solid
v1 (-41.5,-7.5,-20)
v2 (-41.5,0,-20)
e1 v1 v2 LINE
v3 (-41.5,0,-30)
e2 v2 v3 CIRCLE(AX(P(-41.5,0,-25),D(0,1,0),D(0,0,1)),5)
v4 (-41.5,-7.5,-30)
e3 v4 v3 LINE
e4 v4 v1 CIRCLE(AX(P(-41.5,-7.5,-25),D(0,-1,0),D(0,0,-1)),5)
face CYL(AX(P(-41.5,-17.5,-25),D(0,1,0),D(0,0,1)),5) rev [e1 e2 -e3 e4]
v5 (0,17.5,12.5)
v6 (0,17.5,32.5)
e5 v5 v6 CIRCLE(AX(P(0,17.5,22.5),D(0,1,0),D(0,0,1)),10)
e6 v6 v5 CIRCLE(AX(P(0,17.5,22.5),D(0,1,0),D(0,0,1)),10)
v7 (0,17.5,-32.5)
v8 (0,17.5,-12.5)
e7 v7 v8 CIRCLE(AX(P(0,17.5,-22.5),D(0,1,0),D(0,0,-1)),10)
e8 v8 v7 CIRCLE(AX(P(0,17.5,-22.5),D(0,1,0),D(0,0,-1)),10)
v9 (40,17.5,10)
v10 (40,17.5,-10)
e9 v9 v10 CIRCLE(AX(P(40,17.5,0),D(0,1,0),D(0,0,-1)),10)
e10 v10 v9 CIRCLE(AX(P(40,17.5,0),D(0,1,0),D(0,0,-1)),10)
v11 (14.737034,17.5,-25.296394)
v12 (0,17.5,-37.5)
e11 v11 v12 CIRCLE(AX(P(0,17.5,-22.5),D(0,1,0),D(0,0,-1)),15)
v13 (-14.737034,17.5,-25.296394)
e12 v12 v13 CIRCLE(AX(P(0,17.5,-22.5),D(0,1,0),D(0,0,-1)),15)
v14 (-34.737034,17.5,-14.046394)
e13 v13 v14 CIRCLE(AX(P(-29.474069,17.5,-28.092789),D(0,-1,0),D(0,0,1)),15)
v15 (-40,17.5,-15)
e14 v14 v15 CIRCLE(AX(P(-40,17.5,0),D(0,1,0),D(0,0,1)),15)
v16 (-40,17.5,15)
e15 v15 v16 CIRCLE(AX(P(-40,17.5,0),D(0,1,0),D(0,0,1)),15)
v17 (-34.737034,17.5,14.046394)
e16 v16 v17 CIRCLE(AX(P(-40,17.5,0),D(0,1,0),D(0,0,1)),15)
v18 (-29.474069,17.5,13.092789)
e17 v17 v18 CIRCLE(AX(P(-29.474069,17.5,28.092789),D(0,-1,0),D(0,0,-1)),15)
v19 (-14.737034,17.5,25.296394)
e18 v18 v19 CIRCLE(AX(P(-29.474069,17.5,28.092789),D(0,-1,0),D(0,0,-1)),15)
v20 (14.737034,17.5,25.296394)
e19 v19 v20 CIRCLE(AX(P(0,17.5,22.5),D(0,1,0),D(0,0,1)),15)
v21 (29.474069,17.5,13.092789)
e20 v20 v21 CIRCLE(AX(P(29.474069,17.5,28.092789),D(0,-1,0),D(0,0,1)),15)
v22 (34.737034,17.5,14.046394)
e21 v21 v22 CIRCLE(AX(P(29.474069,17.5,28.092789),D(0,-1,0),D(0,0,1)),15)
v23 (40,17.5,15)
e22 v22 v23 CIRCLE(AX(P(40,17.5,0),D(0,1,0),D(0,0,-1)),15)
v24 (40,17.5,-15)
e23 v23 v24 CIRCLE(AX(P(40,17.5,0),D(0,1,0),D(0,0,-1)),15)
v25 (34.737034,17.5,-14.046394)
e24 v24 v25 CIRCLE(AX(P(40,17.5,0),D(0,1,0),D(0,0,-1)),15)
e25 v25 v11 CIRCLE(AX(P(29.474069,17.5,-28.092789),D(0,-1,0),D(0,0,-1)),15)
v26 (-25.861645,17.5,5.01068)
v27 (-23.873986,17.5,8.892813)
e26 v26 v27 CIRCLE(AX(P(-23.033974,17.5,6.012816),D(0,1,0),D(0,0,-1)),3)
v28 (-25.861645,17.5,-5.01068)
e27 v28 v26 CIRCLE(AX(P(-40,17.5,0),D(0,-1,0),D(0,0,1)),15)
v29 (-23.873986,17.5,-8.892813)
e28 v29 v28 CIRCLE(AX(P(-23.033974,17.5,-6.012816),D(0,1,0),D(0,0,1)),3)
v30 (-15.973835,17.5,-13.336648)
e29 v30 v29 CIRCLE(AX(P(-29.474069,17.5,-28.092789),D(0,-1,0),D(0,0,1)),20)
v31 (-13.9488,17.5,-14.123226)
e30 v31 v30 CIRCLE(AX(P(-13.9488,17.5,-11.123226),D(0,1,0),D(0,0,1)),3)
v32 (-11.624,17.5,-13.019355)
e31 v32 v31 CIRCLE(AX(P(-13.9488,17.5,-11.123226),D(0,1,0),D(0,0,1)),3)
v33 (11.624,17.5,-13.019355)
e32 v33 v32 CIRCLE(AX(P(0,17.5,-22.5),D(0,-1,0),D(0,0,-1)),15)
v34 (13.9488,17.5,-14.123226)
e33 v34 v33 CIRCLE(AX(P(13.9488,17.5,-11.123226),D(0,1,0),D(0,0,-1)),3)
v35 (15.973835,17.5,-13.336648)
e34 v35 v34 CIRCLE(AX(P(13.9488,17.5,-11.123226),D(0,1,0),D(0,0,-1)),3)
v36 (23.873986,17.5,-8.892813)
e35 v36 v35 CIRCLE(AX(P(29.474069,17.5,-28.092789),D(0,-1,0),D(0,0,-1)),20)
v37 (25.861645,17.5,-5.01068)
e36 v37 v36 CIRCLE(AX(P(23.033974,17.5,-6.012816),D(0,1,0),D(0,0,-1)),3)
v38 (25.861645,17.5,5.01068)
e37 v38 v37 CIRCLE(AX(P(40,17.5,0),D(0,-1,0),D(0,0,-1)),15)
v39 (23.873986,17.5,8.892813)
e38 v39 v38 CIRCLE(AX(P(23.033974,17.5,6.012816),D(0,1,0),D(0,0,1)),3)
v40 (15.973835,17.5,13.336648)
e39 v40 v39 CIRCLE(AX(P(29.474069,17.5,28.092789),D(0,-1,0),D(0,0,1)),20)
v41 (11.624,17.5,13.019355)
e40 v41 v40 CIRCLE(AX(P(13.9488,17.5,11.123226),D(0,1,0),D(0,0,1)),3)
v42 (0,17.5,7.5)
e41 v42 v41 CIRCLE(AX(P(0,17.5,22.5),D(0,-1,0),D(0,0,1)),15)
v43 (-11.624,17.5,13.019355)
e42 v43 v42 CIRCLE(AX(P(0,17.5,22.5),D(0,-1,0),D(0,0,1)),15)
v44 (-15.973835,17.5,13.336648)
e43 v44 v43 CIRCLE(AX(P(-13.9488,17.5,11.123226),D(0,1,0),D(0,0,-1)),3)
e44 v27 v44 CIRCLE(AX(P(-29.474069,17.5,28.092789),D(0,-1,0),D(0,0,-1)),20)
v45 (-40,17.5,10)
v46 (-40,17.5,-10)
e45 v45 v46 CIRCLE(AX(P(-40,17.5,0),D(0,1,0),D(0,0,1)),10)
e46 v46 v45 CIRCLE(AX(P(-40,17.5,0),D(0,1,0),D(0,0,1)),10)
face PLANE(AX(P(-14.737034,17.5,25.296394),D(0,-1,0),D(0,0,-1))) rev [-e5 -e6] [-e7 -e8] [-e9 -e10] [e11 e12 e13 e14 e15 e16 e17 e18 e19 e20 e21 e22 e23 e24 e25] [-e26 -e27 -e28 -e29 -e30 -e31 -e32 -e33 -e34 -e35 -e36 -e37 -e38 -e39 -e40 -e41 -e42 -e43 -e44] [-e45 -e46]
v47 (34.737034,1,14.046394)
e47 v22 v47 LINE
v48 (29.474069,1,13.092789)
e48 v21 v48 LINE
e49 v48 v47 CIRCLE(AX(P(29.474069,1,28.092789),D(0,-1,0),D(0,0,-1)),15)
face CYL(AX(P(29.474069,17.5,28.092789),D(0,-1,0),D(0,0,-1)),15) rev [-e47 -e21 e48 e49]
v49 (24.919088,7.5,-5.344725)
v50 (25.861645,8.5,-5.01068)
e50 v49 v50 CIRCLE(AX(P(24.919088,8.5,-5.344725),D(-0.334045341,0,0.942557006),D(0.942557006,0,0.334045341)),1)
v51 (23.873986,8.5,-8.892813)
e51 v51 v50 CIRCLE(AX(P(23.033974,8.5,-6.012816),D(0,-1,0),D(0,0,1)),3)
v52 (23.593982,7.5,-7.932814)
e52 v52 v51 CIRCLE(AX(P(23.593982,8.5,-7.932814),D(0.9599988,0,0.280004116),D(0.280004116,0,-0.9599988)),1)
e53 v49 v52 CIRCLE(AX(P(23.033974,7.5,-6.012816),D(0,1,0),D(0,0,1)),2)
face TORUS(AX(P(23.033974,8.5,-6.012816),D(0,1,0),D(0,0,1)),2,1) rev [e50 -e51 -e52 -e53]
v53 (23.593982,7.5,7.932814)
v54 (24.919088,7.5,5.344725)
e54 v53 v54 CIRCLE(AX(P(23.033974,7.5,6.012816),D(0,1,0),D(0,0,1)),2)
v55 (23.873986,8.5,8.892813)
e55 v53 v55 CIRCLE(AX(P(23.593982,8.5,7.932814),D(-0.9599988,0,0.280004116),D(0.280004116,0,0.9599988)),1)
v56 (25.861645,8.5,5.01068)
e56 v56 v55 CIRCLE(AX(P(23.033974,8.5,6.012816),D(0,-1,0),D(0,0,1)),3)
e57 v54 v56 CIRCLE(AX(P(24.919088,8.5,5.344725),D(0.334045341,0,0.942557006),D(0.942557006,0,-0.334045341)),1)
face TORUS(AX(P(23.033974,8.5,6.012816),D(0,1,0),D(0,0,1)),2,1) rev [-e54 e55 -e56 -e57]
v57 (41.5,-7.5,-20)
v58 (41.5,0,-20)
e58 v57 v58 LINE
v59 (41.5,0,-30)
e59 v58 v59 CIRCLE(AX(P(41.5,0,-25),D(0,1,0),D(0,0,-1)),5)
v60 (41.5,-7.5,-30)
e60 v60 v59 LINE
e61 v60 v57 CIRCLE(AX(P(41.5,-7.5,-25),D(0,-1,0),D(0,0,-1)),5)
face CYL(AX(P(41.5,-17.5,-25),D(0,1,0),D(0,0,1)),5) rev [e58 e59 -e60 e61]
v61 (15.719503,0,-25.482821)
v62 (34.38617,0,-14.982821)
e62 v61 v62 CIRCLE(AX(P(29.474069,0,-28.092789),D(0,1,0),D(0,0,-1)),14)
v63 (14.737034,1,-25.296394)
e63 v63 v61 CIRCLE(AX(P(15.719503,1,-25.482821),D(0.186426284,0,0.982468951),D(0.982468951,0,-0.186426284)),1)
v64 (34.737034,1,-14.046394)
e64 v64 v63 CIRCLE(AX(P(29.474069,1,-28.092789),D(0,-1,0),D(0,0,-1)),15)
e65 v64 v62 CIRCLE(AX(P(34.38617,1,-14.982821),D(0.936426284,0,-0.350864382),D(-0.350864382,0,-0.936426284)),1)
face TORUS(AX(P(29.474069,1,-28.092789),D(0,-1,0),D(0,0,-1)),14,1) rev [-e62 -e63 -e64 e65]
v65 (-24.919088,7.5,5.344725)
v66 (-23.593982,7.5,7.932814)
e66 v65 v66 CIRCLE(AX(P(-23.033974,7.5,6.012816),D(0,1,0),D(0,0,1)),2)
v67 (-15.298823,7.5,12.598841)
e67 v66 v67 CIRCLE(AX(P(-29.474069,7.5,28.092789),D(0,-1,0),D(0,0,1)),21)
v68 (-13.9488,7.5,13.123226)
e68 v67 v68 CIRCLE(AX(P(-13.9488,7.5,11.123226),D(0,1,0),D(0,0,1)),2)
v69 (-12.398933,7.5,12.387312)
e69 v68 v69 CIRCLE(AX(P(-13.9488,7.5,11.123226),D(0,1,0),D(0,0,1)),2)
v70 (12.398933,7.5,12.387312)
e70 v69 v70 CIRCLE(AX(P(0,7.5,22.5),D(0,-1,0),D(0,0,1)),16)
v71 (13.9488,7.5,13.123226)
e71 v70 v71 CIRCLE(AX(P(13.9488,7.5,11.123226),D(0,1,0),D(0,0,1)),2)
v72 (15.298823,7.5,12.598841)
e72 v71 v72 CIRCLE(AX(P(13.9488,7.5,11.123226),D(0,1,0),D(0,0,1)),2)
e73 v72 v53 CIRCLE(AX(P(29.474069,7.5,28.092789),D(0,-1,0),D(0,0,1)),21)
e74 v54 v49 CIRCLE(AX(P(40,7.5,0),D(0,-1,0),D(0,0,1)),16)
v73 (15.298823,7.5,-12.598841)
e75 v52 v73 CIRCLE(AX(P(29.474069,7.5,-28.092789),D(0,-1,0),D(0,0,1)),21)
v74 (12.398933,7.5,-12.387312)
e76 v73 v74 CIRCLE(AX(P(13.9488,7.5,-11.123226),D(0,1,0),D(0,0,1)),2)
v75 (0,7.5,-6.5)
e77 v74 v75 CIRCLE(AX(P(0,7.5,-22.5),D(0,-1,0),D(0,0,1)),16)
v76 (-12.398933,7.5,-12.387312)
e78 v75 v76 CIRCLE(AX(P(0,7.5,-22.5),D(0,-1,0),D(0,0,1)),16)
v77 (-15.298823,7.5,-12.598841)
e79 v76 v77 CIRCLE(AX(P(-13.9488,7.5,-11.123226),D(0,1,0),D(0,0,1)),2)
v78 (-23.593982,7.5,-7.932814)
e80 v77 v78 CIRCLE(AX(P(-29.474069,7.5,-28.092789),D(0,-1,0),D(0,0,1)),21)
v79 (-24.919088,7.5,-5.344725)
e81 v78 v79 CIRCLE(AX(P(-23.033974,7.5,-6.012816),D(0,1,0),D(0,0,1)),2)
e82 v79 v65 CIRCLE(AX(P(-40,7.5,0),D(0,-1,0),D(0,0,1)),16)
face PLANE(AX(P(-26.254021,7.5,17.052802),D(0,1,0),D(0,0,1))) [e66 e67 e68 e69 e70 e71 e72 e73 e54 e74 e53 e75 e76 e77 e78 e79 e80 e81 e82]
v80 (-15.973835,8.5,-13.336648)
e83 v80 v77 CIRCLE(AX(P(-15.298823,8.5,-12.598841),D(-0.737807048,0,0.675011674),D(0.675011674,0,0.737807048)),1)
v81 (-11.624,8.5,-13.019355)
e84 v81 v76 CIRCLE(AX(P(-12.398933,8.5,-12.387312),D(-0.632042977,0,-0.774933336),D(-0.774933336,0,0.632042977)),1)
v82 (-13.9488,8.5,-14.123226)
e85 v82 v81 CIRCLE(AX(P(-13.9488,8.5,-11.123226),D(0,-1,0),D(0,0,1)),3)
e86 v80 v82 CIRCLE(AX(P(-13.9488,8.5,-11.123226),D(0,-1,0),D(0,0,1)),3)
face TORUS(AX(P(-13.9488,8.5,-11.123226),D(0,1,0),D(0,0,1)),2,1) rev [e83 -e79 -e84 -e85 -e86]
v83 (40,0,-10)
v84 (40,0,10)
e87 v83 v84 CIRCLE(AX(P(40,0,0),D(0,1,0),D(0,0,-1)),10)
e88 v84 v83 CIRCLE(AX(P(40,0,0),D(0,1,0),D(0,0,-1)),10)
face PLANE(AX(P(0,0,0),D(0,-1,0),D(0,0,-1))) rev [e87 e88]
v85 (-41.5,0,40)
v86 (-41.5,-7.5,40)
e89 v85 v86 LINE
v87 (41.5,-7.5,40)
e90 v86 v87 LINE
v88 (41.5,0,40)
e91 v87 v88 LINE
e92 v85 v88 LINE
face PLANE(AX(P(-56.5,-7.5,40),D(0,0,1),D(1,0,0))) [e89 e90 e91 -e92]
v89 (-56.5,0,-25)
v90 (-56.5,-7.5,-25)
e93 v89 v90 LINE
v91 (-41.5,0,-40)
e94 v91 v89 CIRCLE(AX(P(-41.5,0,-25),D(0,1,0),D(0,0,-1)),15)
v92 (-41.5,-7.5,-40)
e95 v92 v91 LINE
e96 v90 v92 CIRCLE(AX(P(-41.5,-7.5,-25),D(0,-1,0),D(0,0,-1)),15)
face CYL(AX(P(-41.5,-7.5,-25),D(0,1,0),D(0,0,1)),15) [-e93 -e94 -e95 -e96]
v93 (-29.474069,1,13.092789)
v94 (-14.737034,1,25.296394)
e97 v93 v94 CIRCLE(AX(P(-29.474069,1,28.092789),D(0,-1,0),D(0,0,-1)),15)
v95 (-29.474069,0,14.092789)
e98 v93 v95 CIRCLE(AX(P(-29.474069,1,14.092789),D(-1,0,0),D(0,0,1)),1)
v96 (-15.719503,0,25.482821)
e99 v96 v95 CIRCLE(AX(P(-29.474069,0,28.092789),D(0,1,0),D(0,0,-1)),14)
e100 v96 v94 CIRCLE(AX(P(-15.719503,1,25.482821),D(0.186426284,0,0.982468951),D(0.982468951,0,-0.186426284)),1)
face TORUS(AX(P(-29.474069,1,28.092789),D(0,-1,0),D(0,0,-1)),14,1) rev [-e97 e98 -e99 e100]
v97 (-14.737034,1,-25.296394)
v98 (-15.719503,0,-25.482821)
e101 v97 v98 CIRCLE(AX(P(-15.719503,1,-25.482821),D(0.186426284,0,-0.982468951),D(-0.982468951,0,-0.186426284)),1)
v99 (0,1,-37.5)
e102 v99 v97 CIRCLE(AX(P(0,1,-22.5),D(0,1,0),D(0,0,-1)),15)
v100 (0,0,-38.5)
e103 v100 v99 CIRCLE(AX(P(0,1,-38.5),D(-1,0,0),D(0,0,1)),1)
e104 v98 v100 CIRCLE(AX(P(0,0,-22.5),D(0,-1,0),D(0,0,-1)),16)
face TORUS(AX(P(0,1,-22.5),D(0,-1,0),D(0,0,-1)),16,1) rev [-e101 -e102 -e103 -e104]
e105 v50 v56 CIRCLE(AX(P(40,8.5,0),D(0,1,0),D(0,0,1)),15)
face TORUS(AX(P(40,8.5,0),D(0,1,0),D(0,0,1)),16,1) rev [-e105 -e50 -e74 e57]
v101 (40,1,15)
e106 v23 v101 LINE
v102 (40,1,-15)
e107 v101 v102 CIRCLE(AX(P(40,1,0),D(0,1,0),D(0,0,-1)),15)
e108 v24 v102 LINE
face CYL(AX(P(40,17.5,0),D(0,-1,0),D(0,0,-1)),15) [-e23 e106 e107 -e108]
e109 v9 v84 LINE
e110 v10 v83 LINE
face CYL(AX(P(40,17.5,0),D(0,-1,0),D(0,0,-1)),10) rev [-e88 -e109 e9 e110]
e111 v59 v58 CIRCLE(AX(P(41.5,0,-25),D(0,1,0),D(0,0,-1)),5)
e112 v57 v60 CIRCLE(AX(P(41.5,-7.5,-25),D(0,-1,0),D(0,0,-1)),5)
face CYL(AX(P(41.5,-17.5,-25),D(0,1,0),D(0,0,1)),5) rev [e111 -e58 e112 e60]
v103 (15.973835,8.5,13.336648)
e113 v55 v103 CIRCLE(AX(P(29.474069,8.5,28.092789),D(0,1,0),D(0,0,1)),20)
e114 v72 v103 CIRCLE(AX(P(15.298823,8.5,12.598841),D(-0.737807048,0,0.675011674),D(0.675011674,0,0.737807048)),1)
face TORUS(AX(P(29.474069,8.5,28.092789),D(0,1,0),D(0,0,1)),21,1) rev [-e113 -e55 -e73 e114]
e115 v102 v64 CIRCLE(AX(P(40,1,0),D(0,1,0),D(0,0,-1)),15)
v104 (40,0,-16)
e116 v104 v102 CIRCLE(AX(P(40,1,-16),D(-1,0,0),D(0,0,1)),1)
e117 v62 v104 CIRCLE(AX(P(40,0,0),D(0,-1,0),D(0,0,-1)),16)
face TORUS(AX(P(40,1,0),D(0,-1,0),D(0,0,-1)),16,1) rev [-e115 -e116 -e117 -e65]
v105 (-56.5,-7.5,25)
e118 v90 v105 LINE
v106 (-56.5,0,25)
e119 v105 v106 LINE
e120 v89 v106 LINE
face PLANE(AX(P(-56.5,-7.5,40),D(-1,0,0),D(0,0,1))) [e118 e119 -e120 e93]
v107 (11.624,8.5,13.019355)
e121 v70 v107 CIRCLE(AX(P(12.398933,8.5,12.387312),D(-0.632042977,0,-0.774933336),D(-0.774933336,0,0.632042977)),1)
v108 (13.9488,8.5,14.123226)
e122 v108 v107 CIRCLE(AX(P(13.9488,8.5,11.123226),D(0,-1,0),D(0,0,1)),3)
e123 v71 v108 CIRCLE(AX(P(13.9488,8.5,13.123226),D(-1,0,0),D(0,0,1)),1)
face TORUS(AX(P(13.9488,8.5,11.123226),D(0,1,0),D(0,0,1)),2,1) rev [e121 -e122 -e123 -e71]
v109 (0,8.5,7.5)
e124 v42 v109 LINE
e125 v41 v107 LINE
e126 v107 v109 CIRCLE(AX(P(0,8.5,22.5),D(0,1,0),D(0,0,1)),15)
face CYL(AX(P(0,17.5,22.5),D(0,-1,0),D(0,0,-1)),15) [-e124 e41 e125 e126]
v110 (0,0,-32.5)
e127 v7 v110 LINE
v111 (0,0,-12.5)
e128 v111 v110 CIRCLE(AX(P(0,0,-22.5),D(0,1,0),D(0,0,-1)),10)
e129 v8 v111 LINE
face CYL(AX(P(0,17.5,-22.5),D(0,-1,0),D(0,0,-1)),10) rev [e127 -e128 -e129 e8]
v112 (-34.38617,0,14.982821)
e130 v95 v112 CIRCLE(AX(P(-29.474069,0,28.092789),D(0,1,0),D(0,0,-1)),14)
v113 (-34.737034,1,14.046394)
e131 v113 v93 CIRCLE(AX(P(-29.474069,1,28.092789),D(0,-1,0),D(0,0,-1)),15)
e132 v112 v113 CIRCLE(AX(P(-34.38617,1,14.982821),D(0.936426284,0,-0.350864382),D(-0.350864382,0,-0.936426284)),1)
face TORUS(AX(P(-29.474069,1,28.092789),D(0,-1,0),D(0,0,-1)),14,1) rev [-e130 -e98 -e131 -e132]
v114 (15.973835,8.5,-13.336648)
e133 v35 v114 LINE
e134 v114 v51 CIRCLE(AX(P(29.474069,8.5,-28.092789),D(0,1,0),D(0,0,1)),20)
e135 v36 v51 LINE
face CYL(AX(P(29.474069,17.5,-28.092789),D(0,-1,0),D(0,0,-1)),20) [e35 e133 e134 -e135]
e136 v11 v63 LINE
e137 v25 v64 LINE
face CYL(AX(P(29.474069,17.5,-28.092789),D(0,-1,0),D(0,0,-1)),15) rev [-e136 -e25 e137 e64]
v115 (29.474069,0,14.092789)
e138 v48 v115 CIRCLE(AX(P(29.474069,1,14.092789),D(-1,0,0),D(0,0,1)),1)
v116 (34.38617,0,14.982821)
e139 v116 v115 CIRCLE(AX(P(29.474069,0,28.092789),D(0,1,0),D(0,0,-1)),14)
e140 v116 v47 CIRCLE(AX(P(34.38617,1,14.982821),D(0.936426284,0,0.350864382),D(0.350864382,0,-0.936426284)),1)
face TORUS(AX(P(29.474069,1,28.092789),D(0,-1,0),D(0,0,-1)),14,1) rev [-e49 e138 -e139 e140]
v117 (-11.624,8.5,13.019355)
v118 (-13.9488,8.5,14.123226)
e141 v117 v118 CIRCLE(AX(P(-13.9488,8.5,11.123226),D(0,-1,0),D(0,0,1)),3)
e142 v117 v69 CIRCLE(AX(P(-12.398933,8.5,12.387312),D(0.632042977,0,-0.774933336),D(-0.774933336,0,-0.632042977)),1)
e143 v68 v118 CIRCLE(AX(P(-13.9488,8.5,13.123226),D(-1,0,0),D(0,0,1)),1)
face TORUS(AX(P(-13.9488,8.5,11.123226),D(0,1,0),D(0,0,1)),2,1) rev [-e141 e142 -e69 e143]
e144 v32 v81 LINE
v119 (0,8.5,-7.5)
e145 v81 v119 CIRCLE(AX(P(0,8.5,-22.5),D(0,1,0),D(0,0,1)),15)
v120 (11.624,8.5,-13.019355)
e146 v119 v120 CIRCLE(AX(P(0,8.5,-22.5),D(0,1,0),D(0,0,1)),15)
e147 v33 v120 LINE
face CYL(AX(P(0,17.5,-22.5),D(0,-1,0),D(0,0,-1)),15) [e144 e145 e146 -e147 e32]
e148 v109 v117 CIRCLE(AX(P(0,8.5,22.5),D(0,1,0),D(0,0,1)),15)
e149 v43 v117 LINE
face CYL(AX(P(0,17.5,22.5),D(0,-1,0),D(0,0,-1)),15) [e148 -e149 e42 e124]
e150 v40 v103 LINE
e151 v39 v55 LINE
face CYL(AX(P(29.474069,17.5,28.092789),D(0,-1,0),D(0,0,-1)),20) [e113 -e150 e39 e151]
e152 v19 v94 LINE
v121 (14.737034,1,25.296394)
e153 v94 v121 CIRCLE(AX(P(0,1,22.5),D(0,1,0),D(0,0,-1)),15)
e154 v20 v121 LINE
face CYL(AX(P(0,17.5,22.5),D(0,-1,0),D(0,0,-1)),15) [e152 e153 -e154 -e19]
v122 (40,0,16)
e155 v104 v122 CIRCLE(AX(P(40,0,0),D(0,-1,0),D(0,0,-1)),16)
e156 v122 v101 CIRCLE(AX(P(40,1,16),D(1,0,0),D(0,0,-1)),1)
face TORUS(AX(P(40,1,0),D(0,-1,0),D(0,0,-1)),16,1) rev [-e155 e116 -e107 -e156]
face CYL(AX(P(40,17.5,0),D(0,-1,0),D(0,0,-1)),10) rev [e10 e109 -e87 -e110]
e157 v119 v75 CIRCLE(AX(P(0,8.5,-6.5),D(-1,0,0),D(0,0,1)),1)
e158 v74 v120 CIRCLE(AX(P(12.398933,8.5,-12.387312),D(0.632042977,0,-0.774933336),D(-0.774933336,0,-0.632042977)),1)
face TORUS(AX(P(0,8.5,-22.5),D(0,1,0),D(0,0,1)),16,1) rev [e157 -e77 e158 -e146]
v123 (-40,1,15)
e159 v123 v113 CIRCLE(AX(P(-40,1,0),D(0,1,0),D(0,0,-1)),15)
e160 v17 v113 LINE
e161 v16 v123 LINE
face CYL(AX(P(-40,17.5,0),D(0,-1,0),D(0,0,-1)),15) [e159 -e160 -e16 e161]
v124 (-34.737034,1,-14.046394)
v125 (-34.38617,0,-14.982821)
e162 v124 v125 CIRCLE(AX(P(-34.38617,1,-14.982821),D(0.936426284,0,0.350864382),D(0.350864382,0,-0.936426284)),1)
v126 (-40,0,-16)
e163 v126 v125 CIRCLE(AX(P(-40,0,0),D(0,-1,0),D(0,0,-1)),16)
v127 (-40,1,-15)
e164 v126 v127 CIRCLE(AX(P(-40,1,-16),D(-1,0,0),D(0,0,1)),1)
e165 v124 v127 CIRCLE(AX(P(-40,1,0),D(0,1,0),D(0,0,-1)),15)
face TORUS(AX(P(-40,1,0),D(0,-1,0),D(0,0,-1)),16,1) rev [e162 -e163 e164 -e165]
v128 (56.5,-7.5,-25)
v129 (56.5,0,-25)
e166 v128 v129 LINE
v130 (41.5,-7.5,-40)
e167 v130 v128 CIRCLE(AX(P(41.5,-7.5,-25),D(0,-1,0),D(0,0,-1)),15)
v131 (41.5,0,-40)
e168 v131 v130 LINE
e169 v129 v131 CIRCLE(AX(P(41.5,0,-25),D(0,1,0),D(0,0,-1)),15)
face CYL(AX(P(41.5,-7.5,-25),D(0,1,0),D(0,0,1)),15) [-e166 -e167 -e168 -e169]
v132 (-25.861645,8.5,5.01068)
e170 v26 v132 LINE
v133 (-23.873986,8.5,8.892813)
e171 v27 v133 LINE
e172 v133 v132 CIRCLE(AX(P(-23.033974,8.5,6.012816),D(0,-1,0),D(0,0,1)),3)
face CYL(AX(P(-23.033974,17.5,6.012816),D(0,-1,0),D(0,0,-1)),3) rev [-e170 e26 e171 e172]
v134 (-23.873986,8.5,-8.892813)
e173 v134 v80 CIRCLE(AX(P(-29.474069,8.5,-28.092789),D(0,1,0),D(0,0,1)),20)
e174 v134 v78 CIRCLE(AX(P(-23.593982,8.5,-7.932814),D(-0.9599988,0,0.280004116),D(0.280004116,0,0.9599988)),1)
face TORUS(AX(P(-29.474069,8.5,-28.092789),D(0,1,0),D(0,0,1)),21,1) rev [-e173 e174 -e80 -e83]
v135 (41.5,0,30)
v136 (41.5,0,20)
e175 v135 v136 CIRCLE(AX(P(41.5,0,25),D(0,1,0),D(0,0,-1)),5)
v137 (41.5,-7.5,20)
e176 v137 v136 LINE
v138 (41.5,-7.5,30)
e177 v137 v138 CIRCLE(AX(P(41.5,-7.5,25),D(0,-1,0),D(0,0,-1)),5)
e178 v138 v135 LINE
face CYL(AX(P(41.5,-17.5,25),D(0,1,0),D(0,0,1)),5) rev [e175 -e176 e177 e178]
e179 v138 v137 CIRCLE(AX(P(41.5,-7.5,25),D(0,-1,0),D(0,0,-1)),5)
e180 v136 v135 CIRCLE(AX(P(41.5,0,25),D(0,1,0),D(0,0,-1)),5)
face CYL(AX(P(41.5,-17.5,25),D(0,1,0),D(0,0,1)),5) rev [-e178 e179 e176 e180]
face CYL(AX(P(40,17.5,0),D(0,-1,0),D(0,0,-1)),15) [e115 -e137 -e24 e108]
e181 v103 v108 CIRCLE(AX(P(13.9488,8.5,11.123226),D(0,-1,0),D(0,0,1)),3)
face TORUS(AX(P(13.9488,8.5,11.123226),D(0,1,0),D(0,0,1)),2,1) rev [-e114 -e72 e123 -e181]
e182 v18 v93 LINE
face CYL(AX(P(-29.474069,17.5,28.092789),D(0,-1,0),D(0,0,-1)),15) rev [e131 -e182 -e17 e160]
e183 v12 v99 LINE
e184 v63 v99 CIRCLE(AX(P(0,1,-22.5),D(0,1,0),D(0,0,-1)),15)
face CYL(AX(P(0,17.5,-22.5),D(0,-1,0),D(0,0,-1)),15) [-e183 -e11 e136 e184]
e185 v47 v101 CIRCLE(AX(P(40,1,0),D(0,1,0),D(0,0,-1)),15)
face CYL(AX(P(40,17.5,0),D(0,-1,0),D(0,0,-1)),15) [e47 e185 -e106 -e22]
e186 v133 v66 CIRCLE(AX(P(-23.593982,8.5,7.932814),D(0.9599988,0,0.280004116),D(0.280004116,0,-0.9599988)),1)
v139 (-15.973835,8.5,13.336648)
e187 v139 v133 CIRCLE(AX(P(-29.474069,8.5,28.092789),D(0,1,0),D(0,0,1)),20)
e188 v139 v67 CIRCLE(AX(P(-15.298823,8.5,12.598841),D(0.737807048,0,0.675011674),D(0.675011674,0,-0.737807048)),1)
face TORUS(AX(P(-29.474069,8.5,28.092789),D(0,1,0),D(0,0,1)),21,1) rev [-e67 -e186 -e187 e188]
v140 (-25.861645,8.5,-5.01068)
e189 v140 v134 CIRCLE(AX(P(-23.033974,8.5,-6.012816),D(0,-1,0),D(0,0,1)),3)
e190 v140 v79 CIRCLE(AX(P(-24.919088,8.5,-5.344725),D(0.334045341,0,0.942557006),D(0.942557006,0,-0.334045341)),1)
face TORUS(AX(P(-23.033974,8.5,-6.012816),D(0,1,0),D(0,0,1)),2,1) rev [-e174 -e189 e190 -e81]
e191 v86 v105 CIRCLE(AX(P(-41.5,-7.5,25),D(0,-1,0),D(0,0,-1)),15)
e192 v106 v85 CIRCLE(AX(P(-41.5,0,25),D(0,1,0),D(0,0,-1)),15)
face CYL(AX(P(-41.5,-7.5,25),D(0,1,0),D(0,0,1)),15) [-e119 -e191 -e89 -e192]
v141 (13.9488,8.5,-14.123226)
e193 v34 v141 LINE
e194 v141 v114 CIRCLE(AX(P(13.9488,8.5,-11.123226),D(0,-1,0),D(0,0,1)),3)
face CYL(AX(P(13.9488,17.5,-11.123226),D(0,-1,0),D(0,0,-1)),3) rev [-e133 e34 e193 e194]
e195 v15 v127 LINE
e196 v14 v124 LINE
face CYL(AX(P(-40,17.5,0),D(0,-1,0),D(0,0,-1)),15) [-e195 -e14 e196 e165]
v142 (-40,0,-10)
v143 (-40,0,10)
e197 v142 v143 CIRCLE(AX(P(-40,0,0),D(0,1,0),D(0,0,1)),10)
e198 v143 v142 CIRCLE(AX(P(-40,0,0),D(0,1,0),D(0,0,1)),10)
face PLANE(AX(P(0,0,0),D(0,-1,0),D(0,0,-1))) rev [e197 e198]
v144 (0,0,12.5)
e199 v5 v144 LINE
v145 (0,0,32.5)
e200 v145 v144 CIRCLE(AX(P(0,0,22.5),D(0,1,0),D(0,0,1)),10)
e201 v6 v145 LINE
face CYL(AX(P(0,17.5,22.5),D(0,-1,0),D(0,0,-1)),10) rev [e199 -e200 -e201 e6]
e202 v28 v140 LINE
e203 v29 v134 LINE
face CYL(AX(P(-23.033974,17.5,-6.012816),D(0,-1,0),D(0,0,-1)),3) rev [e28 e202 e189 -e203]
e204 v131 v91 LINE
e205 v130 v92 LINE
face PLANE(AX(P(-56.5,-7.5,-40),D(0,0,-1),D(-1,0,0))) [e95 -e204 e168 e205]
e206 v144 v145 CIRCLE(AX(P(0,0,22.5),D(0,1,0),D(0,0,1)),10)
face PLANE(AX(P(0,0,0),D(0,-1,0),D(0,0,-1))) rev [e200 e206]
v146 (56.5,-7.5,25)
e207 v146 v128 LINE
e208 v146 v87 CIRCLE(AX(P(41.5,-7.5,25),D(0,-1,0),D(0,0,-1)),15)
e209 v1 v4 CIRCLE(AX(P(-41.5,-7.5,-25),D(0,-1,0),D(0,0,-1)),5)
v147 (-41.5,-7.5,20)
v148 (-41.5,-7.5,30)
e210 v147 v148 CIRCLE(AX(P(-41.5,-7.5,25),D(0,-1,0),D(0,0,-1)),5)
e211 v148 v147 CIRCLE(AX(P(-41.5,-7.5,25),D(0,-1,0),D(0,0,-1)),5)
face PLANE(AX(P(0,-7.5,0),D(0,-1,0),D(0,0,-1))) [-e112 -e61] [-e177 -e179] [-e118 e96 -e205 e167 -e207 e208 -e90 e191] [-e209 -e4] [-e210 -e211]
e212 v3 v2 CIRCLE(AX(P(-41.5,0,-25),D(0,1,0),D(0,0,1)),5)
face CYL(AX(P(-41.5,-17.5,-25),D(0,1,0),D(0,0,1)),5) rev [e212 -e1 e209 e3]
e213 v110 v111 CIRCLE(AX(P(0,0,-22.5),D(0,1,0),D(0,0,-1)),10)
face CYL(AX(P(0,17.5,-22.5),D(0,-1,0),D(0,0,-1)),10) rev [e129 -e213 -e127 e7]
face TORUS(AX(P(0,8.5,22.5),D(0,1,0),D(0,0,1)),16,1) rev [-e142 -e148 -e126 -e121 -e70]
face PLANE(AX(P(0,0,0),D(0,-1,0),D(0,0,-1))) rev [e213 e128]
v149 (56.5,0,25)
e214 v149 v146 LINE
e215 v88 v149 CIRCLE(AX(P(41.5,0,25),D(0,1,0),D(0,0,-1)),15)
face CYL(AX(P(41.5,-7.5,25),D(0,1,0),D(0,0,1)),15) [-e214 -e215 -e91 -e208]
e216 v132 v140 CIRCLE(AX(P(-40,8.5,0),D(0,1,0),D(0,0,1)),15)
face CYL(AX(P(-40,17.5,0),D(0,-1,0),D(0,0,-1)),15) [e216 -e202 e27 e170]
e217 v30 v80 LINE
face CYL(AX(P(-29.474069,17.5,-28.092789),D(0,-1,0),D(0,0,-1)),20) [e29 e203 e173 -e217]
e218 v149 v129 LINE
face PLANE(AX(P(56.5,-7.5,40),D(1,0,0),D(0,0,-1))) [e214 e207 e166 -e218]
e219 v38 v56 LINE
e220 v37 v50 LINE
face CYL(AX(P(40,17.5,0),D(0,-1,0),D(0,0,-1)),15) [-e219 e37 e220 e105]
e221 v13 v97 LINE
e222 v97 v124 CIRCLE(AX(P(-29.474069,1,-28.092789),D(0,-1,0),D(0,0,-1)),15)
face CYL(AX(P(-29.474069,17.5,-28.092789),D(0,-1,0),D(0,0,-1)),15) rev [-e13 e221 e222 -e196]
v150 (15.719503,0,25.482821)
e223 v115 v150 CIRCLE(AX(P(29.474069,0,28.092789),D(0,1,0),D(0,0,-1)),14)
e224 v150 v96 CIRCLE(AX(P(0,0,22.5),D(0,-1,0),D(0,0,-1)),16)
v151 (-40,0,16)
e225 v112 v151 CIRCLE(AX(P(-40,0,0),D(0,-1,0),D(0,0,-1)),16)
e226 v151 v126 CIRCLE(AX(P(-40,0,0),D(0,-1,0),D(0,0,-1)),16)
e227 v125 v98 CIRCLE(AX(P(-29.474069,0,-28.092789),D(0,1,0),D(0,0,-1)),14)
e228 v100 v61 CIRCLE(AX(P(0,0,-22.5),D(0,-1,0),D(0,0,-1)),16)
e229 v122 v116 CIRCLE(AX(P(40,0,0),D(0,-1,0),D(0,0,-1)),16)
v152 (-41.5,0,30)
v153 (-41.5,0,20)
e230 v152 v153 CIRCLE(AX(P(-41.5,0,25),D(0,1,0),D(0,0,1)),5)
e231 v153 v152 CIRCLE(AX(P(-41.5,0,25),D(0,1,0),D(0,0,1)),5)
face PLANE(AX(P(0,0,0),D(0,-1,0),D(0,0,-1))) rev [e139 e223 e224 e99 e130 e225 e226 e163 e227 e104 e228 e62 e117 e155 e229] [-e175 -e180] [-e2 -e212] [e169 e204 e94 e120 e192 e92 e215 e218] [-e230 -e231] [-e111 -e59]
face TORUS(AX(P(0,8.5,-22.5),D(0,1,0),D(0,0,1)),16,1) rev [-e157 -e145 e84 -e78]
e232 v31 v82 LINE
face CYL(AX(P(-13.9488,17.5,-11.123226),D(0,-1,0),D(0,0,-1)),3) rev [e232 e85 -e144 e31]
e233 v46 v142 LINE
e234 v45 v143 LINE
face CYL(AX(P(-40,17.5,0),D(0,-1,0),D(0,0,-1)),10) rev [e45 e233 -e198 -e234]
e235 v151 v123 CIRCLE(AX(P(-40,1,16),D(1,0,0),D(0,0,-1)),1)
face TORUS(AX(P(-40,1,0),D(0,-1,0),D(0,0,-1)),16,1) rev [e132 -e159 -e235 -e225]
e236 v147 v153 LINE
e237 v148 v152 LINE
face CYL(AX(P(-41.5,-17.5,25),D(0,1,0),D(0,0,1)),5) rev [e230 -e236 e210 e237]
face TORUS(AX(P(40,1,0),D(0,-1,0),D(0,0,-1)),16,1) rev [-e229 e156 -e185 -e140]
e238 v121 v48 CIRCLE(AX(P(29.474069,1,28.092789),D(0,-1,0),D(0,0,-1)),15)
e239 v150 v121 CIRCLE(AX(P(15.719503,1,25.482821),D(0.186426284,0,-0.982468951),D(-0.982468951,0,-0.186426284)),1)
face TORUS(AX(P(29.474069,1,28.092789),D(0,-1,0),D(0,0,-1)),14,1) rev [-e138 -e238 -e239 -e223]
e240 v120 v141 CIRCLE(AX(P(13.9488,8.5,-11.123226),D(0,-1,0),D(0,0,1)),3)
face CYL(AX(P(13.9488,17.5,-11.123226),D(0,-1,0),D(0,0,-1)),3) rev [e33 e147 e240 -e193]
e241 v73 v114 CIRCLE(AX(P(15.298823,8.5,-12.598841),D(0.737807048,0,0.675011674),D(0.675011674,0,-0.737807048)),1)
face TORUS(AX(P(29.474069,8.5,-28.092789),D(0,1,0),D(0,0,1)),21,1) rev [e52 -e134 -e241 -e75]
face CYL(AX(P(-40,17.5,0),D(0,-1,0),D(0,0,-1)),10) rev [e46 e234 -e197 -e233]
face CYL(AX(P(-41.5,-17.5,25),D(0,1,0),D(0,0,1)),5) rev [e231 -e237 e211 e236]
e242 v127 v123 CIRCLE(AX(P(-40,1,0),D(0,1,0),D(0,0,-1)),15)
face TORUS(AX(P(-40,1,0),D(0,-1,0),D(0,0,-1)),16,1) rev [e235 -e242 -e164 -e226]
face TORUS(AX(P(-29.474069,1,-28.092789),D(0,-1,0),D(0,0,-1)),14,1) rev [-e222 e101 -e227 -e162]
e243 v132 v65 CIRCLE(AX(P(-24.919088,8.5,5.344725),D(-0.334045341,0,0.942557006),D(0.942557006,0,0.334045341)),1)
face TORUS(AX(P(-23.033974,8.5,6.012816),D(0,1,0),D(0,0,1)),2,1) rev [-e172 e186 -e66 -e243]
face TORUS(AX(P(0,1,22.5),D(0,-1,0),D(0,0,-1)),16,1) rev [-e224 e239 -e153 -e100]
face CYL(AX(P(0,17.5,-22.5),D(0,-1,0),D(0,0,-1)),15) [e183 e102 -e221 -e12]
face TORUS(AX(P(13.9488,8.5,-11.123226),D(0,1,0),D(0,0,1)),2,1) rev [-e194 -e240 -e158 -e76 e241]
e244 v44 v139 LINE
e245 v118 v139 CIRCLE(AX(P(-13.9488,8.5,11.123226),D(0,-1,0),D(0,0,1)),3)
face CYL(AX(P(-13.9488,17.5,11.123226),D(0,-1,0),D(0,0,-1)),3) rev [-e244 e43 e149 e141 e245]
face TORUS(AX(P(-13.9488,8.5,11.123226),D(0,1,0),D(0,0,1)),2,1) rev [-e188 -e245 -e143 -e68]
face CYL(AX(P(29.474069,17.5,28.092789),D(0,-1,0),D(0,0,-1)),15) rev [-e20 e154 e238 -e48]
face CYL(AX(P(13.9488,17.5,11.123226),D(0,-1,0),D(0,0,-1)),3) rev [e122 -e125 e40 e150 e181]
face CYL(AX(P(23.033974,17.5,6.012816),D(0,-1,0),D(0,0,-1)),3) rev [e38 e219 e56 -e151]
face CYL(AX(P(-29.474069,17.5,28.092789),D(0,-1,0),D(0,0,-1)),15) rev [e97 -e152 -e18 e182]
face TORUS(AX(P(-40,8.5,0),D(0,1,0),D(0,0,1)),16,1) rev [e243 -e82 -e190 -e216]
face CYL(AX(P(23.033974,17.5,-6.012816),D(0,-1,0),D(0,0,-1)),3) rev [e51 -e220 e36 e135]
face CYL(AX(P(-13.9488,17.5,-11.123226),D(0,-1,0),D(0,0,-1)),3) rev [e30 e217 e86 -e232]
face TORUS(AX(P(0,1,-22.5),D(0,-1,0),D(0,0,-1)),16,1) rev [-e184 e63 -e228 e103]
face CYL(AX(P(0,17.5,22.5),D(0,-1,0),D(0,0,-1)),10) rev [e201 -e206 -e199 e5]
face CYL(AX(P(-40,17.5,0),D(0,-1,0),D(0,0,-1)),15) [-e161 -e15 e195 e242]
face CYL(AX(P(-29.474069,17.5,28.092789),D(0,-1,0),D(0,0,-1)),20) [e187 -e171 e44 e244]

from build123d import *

# Parameters (mm, degrees)
BASE_PLATE_SKETCH_W         = 113
BASE_PLATE_SKETCH_H         = 80
BASE_PLATE_113X80X7_5_DEPTH = 7.5
QUAD_BOSS_PROFILE_SKETCH_R  = 10
QUAD_BOSS_BODY_H17_5_DEPTH  = 17.5
BOSS_ROOT_FILLET_R1_R       = 1
PLATE_CORNER_FILLETS_R15_R  = 15
BORE_CUT_SKETCH_R           = 5
BORE_CUTS_D17_5_DEPTH       = 17.5
BOSS_WEB_H7_5_DEPTH         = 7.5
WEB_BLEND_FILLET_R1_R       = 1


with BuildPart() as part:
    # Base Plate Sketch → Base Plate 113x80x7.5 (new body)
    with BuildSketch(Plane(origin=(0, 0, 0), x_dir=(1, 0, 0), z_dir=(0, 1, 0))):
        Rectangle(BASE_PLATE_SKETCH_W, BASE_PLATE_SKETCH_H)
    extrude(amount=-BASE_PLATE_113X80X7_5_DEPTH)

    # Quad Boss Profile Sketch → Quad Boss Body H17.5 (add)
    with BuildSketch(Plane(origin=(0, 0, 0), x_dir=(1, 0, 0), z_dir=(0, 1, 0))):
        with BuildLine():
            ThreePointArc((-34.737034272, 14.046394261), (-55, 0), (-34.737034272, -14.046394261))
            ThreePointArc((-34.737034272, -14.046394261), (-22.12014995, -15.019155466), (-14.737034272, -25.296394261))
            ThreePointArc((-14.737034272, -25.296394261), (0, -37.5), (14.737034272, -25.296394261))
            ThreePointArc((14.737034272, -25.296394261), (22.12014995, -15.019155466), (34.737034272, -14.046394261))
            ThreePointArc((34.737034272, -14.046394261), (55, 0), (34.737034272, 14.046394261))
            ThreePointArc((34.737034272, 14.046394261), (22.12014995, 15.019155466), (14.737034272, 25.296394261))
            ThreePointArc((14.737034272, 25.296394261), (0, 37.5), (-14.737034272, 25.296394261))
            ThreePointArc((-14.737034272, 25.296394261), (-22.12014995, 15.019155466), (-34.737034272, 14.046394261))
        make_face()
        with Locations(Location((-40, 0, 0), (0, 0, 270))):
            Circle(QUAD_BOSS_PROFILE_SKETCH_R, mode=Mode.SUBTRACT)
        with Locations(Location((0, -22.5, 0), (0, 0, 270))):
            Circle(QUAD_BOSS_PROFILE_SKETCH_R, mode=Mode.SUBTRACT)
        with Locations(Location((40, 0, 0), (0, 0, 90))):
            Circle(QUAD_BOSS_PROFILE_SKETCH_R, mode=Mode.SUBTRACT)
        with Locations(Location((0, 22.5, 0), (0, 0, 90))):
            Circle(QUAD_BOSS_PROFILE_SKETCH_R, mode=Mode.SUBTRACT)
        with BuildLine():
            ThreePointArc((25.861644904, -5.01068011), (25, 0), (25.861644904, 5.01068011))
            ThreePointArc((25.861644904, 5.01068011), (25.704313442, 7.380034713), (23.873986231, 8.892812531))
            ThreePointArc((23.873986231, 8.892812531), (19.668843751, 10.66127778), (15.97383507, 13.336647559))
            ThreePointArc((15.97383507, 13.336647559), (13.730549392, 14.115276991), (11.62400004, 13.019355346))
            ThreePointArc((11.62400004, 13.019355346), (0, 7.5), (-11.62400004, 13.019355346))
            ThreePointArc((-11.62400004, 13.019355346), (-13.730549392, 14.115276991), (-15.97383507, 13.336647559))
            ThreePointArc((-15.97383507, 13.336647559), (-19.668843751, 10.66127778), (-23.873986231, 8.892812531))
            ThreePointArc((-23.873986231, 8.892812531), (-25.704313442, 7.380034713), (-25.861644904, 5.01068011))
            ThreePointArc((-25.861644904, 5.01068011), (-25, 0), (-25.861644904, -5.01068011))
            ThreePointArc((-25.861644904, -5.01068011), (-25.704313442, -7.380034713), (-23.873986231, -8.892812531))
            ThreePointArc((-23.873986231, -8.892812531), (-19.668843751, -10.66127778), (-15.97383507, -13.336647559))
            ThreePointArc((-15.97383507, -13.336647559), (-13.730549392, -14.115276991), (-11.62400004, -13.019355346))
            ThreePointArc((-11.62400004, -13.019355346), (0, -7.5), (11.62400004, -13.019355346))
            ThreePointArc((11.62400004, -13.019355346), (13.730549392, -14.115276991), (15.97383507, -13.336647559))
            ThreePointArc((15.97383507, -13.336647559), (19.668843751, -10.66127778), (23.873986231, -8.892812531))
            ThreePointArc((23.873986231, -8.892812531), (25.704313442, -7.380034713), (25.861644904, -5.01068011))
        make_face(mode=Mode.SUBTRACT)
    extrude(amount=QUAD_BOSS_BODY_H17_5_DEPTH)

    # Boss Root Fillet R1
    boss_root_fillet_r1_edges = [part.edges().sort_by_distance(p)[0] for p in [
        (-22.12014995, 0, 15.019155466),
        (0, 0, 37.5),
        (22.12014995, 0, 15.019155466),
        (55, 0, 0),
        (22.12014995, 0, -15.019155466),
        (0, 0, -37.5),
        (-22.12014995, 0, -15.019155466),
        (-55, 0, 0),
    ]]
    fillet(boss_root_fillet_r1_edges, radius=BOSS_ROOT_FILLET_R1_R)

    # Plate Corner Fillets R15
    plate_corner_fillets_r15_edges = [part.edges().sort_by_distance(p)[0] for p in [
        (56.5, -3.75, 40),
        (-56.5, -3.75, 40),
        (-56.5, -3.75, -40),
        (56.5, -3.75, -40),
    ]]
    fillet(plate_corner_fillets_r15_edges, radius=PLATE_CORNER_FILLETS_R15_R)

    # Bore Cut Sketch → Bore Cuts D17.5 (cut)
    with BuildSketch(Plane(origin=(0, 0, 0), x_dir=(1, 0, 0), z_dir=(0, 1, 0))):
        with Locations(Location((-41.5, 25, 0), (0, 0, 270))):
            Circle(BORE_CUT_SKETCH_R)
        with Locations(Location((-41.5, -25, 0), (0, 0, 270))):
            Circle(BORE_CUT_SKETCH_R)
        with Locations(Location((41.5, -25, 0), (0, 0, 90))):
            Circle(BORE_CUT_SKETCH_R)
        with Locations(Location((41.5, 25, 0), (0, 0, 90))):
            Circle(BORE_CUT_SKETCH_R)
    extrude(amount=-BORE_CUTS_D17_5_DEPTH, mode=Mode.SUBTRACT)

    # Boss Web Offset Sketch → Boss Web H7.5 (add)
    with BuildSketch(Plane(origin=(0, 0, 0), x_dir=(1, 0, 0), z_dir=(0, 1, 0))):
        with BuildLine():
            ThreePointArc((-15.97383507, -13.336647559), (-13.730549392, -14.115276991), (-11.62400004, -13.019355346))
            ThreePointArc((-11.62400004, -13.019355346), (0, -7.5), (11.62400004, -13.019355346))
            ThreePointArc((11.62400004, -13.019355346), (13.730549392, -14.115276991), (15.97383507, -13.336647559))
            ThreePointArc((15.97383507, -13.336647559), (19.668843751, -10.66127778), (23.873986231, -8.892812531))
            ThreePointArc((23.873986231, -8.892812531), (25.704313442, -7.380034713), (25.861644904, -5.01068011))
            ThreePointArc((25.861644904, -5.01068011), (25, 0), (25.861644904, 5.01068011))
            ThreePointArc((25.861644904, 5.01068011), (25.704313442, 7.380034713), (23.873986231, 8.892812531))
            ThreePointArc((23.873986231, 8.892812531), (19.668843751, 10.66127778), (15.97383507, 13.336647559))
            ThreePointArc((15.97383507, 13.336647559), (13.730549392, 14.115276991), (11.62400004, 13.019355346))
            ThreePointArc((11.62400004, 13.019355346), (0, 7.5), (-11.62400004, 13.019355346))
            ThreePointArc((-11.62400004, 13.019355346), (-13.730549392, 14.115276991), (-15.97383507, 13.336647559))
            ThreePointArc((-15.97383507, 13.336647559), (-19.668843751, 10.66127778), (-23.873986231, 8.892812531))
            ThreePointArc((-23.873986231, 8.892812531), (-25.704313442, 7.380034713), (-25.861644904, 5.01068011))
            ThreePointArc((-25.861644904, 5.01068011), (-25, 0), (-25.861644904, -5.01068011))
            ThreePointArc((-25.861644904, -5.01068011), (-25.704313442, -7.380034713), (-23.873986231, -8.892812531))
            ThreePointArc((-23.873986231, -8.892812531), (-19.668843751, -10.66127778), (-15.97383507, -13.336647559))
        make_face()
    extrude(amount=BOSS_WEB_H7_5_DEPTH)

    # Web Blend Fillet R1
    web_blend_fillet_r1_edges = [part.edges().sort_by_distance(p)[0] for p in [
        (-19.668843751, 7.5, 10.66127778),
        (-13.730549392, 7.5, 14.115276991),
        (0, 7.5, 7.5),
        (13.730549392, 7.5, 14.115276991),
        (19.668843751, 7.5, 10.66127778),
        (25.704313442, 7.5, 7.380034713),
        (25, 7.5, 0),
        (25.704313442, 7.5, -7.380034713),
        (19.668843751, 7.5, -10.66127778),
        (13.730549392, 7.5, -14.115276991),
        (0, 7.5, -7.5),
        (-13.730549392, 7.5, -14.115276991),
        (-19.668843751, 7.5, -10.66127778),
        (-25.704313442, 7.5, -7.380034713),
        (-25, 7.5, 0),
        (-25.704313442, 7.5, 7.380034713),
    ]]
    fillet(web_blend_fillet_r1_edges, radius=WEB_BLEND_FILLET_R1_R)


solid = part.part
